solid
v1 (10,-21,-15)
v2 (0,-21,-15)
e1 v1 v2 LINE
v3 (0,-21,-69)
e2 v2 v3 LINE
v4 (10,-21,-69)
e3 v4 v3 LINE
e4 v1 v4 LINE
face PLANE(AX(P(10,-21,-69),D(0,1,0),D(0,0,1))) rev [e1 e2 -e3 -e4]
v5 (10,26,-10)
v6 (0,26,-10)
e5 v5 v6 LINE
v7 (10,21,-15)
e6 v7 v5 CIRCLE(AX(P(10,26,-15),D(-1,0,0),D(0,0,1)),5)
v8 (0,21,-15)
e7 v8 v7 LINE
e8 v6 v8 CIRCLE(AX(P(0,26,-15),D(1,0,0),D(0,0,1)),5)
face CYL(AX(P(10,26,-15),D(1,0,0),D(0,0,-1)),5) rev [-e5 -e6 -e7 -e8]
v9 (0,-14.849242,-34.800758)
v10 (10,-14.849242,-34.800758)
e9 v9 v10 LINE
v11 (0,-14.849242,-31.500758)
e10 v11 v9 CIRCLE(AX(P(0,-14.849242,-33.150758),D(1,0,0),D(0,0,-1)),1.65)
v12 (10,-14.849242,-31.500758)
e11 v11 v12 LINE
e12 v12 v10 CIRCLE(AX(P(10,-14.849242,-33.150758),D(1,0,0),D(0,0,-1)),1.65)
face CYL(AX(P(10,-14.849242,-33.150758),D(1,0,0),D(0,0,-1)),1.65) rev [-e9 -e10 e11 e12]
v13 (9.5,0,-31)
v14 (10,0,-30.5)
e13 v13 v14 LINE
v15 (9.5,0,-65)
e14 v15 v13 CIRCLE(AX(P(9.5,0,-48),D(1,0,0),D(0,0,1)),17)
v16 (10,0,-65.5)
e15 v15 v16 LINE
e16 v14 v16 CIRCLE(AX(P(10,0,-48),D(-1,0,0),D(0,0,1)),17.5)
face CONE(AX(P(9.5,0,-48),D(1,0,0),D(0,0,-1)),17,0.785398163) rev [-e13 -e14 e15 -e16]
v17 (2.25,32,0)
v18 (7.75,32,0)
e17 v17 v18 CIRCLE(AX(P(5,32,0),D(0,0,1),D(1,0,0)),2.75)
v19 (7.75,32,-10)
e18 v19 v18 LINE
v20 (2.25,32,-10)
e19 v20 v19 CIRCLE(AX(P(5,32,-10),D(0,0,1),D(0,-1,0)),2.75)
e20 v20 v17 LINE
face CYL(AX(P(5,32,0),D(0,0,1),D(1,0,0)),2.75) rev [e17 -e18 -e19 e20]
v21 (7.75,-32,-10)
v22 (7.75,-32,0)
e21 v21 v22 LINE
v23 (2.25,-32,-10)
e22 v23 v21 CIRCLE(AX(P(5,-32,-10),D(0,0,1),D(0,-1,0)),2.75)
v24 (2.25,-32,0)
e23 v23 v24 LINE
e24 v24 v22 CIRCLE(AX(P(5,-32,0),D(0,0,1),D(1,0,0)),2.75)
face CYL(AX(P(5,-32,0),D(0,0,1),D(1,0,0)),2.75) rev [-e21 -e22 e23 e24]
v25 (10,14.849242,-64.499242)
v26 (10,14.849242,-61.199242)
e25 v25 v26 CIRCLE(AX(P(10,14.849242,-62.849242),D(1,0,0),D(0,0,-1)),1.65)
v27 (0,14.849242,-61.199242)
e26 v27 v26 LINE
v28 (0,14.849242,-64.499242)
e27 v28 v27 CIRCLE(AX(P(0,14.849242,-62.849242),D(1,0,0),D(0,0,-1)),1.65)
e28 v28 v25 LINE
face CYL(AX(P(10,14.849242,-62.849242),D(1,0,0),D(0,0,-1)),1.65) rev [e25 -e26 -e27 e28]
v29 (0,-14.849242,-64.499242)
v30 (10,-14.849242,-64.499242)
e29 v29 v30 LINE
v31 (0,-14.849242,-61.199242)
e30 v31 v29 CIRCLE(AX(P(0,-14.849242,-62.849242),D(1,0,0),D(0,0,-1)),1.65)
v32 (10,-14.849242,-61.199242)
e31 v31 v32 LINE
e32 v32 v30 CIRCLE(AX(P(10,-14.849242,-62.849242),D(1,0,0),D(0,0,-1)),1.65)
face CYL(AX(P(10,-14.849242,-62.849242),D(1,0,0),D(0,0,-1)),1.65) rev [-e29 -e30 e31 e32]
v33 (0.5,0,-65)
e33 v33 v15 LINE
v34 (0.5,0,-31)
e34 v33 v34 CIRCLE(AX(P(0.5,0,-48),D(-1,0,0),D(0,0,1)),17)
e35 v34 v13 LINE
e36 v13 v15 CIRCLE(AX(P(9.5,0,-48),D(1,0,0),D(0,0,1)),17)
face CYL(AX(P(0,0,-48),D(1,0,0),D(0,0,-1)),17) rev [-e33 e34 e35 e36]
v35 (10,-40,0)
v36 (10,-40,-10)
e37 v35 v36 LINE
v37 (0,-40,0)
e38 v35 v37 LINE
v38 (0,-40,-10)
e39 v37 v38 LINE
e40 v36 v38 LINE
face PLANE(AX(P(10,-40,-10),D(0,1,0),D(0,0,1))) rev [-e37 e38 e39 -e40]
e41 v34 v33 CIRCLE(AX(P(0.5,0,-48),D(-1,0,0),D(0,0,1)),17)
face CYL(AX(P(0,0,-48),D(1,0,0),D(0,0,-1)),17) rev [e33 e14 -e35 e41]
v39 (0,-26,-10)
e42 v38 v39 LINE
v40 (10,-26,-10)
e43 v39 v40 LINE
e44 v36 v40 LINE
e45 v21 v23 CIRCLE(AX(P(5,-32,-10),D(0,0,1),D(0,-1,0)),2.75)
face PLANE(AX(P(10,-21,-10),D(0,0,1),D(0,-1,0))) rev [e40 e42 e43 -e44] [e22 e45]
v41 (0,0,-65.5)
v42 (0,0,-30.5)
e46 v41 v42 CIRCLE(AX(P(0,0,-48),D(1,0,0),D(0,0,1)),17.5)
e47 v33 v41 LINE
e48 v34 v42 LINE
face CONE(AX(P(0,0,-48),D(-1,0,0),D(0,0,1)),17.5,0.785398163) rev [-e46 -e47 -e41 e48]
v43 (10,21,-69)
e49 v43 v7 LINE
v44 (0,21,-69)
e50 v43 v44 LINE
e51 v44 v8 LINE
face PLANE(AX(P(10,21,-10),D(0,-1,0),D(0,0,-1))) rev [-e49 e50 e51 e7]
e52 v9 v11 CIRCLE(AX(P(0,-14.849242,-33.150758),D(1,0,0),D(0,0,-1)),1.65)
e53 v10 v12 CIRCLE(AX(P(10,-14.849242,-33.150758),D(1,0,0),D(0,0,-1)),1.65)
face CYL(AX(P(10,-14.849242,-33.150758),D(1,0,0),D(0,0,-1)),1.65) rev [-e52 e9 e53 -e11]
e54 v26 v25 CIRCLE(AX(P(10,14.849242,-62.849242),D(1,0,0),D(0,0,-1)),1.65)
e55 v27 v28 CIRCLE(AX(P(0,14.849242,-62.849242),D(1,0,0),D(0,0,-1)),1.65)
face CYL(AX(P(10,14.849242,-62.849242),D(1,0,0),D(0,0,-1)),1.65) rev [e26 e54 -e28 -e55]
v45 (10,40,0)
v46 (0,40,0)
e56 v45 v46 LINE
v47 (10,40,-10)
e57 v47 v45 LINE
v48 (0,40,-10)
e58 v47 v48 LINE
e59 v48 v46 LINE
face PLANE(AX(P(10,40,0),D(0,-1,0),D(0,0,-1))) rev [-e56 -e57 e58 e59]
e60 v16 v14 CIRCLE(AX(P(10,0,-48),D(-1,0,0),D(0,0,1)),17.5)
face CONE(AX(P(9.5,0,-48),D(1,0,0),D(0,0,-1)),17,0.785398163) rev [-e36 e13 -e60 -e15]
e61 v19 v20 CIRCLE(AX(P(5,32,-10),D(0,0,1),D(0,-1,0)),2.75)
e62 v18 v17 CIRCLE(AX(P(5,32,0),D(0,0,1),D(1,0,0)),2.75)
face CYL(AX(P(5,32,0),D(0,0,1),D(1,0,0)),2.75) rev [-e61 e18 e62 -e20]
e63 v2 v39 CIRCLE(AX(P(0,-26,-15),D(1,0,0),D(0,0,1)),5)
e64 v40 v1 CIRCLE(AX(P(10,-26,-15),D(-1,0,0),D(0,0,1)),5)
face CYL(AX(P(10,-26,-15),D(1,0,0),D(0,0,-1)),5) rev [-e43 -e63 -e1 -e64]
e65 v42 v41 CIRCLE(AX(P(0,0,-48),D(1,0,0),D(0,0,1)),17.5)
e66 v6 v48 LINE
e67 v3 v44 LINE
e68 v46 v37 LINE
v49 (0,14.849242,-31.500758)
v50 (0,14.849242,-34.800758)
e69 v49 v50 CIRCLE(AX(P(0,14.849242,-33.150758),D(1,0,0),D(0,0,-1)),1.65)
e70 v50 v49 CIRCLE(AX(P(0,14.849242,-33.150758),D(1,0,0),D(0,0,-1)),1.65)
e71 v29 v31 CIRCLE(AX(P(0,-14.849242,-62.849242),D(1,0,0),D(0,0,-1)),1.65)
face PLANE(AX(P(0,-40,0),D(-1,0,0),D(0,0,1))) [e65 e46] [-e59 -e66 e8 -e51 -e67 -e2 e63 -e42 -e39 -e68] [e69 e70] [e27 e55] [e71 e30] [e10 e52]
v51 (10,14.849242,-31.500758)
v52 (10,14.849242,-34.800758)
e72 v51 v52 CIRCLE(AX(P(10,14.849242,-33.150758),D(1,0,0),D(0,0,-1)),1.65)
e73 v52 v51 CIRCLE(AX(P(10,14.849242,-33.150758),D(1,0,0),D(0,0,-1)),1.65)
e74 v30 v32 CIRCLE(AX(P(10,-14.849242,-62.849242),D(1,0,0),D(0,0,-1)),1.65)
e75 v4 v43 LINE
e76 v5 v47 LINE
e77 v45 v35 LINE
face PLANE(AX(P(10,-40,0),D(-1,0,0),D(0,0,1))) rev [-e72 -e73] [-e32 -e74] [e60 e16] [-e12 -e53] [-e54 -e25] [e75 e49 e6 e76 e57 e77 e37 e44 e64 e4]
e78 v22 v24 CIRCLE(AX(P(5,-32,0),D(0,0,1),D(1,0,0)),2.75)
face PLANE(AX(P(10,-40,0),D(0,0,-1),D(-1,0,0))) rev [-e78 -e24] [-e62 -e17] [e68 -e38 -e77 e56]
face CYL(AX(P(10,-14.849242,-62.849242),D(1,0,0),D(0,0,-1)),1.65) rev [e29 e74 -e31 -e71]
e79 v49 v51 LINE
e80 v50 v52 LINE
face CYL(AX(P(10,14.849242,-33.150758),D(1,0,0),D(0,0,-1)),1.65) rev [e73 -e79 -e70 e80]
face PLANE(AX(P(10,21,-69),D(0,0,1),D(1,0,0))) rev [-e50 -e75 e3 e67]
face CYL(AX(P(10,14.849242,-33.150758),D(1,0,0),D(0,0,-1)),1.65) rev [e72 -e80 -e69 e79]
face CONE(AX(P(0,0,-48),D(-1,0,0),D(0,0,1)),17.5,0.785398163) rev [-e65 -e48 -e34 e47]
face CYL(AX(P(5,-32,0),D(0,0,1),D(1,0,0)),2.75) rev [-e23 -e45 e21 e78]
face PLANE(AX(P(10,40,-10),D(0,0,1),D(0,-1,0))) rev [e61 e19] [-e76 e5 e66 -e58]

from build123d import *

# Parameters (mm, degrees)
BOSS_EXTRUDE1_DEPTH        = 10
SKETCH2_R                  = 17
CUT_EXTRUDE1_DEPTH         = 81.380345856
F_5_5_5_5_DIAMETER_HOLE1_D = 5.5
M4_TAPPED_HOLE1_D          = 3.3
FILLET1_R                  = 5
CHAMFER1_SIZE              = 0.5


with BuildPart() as part:
    # Sketch1 → Boss-Extrude1 (new body)
    with BuildSketch(Plane(origin=(0, 0, 0), x_dir=(0, 0, -1), z_dir=(1, 0, 0))):
        Polygon((0, -40), (0, 40), (10, 40), (10, 21), (69, 21), (69, -21), (10, -21), (10, -40), align=None)
    extrude(amount=BOSS_EXTRUDE1_DEPTH)

    # Sketch2 → Cut-Extrude1 (cut, through all)
    with BuildSketch(Plane(origin=(10, 0, 0), x_dir=(0, 0, -1), z_dir=(1, 0, 0))):
        with Locations((48, 0)):
            Circle(SKETCH2_R)
    extrude(amount=-CUT_EXTRUDE1_DEPTH, mode=Mode.SUBTRACT)

    # Ø5.5 (5.5) Diameter Hole1 (through all)
    with Locations(Plane.XY):
        with Locations((5, 32), (5, -32)):
            Hole(F_5_5_5_5_DIAMETER_HOLE1_D / 2)

    # M4 Tapped Hole1 (through all)
    with Locations(Plane(origin=(10, 0, 0), x_dir=(0, 0, -1), z_dir=(1, 0, 0))):
        with Locations((33.150757595, 14.849242405), (62.849242405, 14.849242405), (62.849242405, -14.849242405), (33.150757595, -14.849242405)):
            Hole(M4_TAPPED_HOLE1_D / 2)

    # Fillet1
    fillet1_edges = [part.edges().sort_by_distance(p)[0] for p in [
        (5, 21, -10),
        (5, -21, -10),
    ]]
    fillet(fillet1_edges, radius=FILLET1_R)

    # Chamfer1
    chamfer1_edges = [part.edges().sort_by_distance(p)[0] for p in [
        (0, 0, -31),
        (10, 0, -31),
    ]]
    chamfer(chamfer1_edges, length=CHAMFER1_SIZE)


solid = part.part
